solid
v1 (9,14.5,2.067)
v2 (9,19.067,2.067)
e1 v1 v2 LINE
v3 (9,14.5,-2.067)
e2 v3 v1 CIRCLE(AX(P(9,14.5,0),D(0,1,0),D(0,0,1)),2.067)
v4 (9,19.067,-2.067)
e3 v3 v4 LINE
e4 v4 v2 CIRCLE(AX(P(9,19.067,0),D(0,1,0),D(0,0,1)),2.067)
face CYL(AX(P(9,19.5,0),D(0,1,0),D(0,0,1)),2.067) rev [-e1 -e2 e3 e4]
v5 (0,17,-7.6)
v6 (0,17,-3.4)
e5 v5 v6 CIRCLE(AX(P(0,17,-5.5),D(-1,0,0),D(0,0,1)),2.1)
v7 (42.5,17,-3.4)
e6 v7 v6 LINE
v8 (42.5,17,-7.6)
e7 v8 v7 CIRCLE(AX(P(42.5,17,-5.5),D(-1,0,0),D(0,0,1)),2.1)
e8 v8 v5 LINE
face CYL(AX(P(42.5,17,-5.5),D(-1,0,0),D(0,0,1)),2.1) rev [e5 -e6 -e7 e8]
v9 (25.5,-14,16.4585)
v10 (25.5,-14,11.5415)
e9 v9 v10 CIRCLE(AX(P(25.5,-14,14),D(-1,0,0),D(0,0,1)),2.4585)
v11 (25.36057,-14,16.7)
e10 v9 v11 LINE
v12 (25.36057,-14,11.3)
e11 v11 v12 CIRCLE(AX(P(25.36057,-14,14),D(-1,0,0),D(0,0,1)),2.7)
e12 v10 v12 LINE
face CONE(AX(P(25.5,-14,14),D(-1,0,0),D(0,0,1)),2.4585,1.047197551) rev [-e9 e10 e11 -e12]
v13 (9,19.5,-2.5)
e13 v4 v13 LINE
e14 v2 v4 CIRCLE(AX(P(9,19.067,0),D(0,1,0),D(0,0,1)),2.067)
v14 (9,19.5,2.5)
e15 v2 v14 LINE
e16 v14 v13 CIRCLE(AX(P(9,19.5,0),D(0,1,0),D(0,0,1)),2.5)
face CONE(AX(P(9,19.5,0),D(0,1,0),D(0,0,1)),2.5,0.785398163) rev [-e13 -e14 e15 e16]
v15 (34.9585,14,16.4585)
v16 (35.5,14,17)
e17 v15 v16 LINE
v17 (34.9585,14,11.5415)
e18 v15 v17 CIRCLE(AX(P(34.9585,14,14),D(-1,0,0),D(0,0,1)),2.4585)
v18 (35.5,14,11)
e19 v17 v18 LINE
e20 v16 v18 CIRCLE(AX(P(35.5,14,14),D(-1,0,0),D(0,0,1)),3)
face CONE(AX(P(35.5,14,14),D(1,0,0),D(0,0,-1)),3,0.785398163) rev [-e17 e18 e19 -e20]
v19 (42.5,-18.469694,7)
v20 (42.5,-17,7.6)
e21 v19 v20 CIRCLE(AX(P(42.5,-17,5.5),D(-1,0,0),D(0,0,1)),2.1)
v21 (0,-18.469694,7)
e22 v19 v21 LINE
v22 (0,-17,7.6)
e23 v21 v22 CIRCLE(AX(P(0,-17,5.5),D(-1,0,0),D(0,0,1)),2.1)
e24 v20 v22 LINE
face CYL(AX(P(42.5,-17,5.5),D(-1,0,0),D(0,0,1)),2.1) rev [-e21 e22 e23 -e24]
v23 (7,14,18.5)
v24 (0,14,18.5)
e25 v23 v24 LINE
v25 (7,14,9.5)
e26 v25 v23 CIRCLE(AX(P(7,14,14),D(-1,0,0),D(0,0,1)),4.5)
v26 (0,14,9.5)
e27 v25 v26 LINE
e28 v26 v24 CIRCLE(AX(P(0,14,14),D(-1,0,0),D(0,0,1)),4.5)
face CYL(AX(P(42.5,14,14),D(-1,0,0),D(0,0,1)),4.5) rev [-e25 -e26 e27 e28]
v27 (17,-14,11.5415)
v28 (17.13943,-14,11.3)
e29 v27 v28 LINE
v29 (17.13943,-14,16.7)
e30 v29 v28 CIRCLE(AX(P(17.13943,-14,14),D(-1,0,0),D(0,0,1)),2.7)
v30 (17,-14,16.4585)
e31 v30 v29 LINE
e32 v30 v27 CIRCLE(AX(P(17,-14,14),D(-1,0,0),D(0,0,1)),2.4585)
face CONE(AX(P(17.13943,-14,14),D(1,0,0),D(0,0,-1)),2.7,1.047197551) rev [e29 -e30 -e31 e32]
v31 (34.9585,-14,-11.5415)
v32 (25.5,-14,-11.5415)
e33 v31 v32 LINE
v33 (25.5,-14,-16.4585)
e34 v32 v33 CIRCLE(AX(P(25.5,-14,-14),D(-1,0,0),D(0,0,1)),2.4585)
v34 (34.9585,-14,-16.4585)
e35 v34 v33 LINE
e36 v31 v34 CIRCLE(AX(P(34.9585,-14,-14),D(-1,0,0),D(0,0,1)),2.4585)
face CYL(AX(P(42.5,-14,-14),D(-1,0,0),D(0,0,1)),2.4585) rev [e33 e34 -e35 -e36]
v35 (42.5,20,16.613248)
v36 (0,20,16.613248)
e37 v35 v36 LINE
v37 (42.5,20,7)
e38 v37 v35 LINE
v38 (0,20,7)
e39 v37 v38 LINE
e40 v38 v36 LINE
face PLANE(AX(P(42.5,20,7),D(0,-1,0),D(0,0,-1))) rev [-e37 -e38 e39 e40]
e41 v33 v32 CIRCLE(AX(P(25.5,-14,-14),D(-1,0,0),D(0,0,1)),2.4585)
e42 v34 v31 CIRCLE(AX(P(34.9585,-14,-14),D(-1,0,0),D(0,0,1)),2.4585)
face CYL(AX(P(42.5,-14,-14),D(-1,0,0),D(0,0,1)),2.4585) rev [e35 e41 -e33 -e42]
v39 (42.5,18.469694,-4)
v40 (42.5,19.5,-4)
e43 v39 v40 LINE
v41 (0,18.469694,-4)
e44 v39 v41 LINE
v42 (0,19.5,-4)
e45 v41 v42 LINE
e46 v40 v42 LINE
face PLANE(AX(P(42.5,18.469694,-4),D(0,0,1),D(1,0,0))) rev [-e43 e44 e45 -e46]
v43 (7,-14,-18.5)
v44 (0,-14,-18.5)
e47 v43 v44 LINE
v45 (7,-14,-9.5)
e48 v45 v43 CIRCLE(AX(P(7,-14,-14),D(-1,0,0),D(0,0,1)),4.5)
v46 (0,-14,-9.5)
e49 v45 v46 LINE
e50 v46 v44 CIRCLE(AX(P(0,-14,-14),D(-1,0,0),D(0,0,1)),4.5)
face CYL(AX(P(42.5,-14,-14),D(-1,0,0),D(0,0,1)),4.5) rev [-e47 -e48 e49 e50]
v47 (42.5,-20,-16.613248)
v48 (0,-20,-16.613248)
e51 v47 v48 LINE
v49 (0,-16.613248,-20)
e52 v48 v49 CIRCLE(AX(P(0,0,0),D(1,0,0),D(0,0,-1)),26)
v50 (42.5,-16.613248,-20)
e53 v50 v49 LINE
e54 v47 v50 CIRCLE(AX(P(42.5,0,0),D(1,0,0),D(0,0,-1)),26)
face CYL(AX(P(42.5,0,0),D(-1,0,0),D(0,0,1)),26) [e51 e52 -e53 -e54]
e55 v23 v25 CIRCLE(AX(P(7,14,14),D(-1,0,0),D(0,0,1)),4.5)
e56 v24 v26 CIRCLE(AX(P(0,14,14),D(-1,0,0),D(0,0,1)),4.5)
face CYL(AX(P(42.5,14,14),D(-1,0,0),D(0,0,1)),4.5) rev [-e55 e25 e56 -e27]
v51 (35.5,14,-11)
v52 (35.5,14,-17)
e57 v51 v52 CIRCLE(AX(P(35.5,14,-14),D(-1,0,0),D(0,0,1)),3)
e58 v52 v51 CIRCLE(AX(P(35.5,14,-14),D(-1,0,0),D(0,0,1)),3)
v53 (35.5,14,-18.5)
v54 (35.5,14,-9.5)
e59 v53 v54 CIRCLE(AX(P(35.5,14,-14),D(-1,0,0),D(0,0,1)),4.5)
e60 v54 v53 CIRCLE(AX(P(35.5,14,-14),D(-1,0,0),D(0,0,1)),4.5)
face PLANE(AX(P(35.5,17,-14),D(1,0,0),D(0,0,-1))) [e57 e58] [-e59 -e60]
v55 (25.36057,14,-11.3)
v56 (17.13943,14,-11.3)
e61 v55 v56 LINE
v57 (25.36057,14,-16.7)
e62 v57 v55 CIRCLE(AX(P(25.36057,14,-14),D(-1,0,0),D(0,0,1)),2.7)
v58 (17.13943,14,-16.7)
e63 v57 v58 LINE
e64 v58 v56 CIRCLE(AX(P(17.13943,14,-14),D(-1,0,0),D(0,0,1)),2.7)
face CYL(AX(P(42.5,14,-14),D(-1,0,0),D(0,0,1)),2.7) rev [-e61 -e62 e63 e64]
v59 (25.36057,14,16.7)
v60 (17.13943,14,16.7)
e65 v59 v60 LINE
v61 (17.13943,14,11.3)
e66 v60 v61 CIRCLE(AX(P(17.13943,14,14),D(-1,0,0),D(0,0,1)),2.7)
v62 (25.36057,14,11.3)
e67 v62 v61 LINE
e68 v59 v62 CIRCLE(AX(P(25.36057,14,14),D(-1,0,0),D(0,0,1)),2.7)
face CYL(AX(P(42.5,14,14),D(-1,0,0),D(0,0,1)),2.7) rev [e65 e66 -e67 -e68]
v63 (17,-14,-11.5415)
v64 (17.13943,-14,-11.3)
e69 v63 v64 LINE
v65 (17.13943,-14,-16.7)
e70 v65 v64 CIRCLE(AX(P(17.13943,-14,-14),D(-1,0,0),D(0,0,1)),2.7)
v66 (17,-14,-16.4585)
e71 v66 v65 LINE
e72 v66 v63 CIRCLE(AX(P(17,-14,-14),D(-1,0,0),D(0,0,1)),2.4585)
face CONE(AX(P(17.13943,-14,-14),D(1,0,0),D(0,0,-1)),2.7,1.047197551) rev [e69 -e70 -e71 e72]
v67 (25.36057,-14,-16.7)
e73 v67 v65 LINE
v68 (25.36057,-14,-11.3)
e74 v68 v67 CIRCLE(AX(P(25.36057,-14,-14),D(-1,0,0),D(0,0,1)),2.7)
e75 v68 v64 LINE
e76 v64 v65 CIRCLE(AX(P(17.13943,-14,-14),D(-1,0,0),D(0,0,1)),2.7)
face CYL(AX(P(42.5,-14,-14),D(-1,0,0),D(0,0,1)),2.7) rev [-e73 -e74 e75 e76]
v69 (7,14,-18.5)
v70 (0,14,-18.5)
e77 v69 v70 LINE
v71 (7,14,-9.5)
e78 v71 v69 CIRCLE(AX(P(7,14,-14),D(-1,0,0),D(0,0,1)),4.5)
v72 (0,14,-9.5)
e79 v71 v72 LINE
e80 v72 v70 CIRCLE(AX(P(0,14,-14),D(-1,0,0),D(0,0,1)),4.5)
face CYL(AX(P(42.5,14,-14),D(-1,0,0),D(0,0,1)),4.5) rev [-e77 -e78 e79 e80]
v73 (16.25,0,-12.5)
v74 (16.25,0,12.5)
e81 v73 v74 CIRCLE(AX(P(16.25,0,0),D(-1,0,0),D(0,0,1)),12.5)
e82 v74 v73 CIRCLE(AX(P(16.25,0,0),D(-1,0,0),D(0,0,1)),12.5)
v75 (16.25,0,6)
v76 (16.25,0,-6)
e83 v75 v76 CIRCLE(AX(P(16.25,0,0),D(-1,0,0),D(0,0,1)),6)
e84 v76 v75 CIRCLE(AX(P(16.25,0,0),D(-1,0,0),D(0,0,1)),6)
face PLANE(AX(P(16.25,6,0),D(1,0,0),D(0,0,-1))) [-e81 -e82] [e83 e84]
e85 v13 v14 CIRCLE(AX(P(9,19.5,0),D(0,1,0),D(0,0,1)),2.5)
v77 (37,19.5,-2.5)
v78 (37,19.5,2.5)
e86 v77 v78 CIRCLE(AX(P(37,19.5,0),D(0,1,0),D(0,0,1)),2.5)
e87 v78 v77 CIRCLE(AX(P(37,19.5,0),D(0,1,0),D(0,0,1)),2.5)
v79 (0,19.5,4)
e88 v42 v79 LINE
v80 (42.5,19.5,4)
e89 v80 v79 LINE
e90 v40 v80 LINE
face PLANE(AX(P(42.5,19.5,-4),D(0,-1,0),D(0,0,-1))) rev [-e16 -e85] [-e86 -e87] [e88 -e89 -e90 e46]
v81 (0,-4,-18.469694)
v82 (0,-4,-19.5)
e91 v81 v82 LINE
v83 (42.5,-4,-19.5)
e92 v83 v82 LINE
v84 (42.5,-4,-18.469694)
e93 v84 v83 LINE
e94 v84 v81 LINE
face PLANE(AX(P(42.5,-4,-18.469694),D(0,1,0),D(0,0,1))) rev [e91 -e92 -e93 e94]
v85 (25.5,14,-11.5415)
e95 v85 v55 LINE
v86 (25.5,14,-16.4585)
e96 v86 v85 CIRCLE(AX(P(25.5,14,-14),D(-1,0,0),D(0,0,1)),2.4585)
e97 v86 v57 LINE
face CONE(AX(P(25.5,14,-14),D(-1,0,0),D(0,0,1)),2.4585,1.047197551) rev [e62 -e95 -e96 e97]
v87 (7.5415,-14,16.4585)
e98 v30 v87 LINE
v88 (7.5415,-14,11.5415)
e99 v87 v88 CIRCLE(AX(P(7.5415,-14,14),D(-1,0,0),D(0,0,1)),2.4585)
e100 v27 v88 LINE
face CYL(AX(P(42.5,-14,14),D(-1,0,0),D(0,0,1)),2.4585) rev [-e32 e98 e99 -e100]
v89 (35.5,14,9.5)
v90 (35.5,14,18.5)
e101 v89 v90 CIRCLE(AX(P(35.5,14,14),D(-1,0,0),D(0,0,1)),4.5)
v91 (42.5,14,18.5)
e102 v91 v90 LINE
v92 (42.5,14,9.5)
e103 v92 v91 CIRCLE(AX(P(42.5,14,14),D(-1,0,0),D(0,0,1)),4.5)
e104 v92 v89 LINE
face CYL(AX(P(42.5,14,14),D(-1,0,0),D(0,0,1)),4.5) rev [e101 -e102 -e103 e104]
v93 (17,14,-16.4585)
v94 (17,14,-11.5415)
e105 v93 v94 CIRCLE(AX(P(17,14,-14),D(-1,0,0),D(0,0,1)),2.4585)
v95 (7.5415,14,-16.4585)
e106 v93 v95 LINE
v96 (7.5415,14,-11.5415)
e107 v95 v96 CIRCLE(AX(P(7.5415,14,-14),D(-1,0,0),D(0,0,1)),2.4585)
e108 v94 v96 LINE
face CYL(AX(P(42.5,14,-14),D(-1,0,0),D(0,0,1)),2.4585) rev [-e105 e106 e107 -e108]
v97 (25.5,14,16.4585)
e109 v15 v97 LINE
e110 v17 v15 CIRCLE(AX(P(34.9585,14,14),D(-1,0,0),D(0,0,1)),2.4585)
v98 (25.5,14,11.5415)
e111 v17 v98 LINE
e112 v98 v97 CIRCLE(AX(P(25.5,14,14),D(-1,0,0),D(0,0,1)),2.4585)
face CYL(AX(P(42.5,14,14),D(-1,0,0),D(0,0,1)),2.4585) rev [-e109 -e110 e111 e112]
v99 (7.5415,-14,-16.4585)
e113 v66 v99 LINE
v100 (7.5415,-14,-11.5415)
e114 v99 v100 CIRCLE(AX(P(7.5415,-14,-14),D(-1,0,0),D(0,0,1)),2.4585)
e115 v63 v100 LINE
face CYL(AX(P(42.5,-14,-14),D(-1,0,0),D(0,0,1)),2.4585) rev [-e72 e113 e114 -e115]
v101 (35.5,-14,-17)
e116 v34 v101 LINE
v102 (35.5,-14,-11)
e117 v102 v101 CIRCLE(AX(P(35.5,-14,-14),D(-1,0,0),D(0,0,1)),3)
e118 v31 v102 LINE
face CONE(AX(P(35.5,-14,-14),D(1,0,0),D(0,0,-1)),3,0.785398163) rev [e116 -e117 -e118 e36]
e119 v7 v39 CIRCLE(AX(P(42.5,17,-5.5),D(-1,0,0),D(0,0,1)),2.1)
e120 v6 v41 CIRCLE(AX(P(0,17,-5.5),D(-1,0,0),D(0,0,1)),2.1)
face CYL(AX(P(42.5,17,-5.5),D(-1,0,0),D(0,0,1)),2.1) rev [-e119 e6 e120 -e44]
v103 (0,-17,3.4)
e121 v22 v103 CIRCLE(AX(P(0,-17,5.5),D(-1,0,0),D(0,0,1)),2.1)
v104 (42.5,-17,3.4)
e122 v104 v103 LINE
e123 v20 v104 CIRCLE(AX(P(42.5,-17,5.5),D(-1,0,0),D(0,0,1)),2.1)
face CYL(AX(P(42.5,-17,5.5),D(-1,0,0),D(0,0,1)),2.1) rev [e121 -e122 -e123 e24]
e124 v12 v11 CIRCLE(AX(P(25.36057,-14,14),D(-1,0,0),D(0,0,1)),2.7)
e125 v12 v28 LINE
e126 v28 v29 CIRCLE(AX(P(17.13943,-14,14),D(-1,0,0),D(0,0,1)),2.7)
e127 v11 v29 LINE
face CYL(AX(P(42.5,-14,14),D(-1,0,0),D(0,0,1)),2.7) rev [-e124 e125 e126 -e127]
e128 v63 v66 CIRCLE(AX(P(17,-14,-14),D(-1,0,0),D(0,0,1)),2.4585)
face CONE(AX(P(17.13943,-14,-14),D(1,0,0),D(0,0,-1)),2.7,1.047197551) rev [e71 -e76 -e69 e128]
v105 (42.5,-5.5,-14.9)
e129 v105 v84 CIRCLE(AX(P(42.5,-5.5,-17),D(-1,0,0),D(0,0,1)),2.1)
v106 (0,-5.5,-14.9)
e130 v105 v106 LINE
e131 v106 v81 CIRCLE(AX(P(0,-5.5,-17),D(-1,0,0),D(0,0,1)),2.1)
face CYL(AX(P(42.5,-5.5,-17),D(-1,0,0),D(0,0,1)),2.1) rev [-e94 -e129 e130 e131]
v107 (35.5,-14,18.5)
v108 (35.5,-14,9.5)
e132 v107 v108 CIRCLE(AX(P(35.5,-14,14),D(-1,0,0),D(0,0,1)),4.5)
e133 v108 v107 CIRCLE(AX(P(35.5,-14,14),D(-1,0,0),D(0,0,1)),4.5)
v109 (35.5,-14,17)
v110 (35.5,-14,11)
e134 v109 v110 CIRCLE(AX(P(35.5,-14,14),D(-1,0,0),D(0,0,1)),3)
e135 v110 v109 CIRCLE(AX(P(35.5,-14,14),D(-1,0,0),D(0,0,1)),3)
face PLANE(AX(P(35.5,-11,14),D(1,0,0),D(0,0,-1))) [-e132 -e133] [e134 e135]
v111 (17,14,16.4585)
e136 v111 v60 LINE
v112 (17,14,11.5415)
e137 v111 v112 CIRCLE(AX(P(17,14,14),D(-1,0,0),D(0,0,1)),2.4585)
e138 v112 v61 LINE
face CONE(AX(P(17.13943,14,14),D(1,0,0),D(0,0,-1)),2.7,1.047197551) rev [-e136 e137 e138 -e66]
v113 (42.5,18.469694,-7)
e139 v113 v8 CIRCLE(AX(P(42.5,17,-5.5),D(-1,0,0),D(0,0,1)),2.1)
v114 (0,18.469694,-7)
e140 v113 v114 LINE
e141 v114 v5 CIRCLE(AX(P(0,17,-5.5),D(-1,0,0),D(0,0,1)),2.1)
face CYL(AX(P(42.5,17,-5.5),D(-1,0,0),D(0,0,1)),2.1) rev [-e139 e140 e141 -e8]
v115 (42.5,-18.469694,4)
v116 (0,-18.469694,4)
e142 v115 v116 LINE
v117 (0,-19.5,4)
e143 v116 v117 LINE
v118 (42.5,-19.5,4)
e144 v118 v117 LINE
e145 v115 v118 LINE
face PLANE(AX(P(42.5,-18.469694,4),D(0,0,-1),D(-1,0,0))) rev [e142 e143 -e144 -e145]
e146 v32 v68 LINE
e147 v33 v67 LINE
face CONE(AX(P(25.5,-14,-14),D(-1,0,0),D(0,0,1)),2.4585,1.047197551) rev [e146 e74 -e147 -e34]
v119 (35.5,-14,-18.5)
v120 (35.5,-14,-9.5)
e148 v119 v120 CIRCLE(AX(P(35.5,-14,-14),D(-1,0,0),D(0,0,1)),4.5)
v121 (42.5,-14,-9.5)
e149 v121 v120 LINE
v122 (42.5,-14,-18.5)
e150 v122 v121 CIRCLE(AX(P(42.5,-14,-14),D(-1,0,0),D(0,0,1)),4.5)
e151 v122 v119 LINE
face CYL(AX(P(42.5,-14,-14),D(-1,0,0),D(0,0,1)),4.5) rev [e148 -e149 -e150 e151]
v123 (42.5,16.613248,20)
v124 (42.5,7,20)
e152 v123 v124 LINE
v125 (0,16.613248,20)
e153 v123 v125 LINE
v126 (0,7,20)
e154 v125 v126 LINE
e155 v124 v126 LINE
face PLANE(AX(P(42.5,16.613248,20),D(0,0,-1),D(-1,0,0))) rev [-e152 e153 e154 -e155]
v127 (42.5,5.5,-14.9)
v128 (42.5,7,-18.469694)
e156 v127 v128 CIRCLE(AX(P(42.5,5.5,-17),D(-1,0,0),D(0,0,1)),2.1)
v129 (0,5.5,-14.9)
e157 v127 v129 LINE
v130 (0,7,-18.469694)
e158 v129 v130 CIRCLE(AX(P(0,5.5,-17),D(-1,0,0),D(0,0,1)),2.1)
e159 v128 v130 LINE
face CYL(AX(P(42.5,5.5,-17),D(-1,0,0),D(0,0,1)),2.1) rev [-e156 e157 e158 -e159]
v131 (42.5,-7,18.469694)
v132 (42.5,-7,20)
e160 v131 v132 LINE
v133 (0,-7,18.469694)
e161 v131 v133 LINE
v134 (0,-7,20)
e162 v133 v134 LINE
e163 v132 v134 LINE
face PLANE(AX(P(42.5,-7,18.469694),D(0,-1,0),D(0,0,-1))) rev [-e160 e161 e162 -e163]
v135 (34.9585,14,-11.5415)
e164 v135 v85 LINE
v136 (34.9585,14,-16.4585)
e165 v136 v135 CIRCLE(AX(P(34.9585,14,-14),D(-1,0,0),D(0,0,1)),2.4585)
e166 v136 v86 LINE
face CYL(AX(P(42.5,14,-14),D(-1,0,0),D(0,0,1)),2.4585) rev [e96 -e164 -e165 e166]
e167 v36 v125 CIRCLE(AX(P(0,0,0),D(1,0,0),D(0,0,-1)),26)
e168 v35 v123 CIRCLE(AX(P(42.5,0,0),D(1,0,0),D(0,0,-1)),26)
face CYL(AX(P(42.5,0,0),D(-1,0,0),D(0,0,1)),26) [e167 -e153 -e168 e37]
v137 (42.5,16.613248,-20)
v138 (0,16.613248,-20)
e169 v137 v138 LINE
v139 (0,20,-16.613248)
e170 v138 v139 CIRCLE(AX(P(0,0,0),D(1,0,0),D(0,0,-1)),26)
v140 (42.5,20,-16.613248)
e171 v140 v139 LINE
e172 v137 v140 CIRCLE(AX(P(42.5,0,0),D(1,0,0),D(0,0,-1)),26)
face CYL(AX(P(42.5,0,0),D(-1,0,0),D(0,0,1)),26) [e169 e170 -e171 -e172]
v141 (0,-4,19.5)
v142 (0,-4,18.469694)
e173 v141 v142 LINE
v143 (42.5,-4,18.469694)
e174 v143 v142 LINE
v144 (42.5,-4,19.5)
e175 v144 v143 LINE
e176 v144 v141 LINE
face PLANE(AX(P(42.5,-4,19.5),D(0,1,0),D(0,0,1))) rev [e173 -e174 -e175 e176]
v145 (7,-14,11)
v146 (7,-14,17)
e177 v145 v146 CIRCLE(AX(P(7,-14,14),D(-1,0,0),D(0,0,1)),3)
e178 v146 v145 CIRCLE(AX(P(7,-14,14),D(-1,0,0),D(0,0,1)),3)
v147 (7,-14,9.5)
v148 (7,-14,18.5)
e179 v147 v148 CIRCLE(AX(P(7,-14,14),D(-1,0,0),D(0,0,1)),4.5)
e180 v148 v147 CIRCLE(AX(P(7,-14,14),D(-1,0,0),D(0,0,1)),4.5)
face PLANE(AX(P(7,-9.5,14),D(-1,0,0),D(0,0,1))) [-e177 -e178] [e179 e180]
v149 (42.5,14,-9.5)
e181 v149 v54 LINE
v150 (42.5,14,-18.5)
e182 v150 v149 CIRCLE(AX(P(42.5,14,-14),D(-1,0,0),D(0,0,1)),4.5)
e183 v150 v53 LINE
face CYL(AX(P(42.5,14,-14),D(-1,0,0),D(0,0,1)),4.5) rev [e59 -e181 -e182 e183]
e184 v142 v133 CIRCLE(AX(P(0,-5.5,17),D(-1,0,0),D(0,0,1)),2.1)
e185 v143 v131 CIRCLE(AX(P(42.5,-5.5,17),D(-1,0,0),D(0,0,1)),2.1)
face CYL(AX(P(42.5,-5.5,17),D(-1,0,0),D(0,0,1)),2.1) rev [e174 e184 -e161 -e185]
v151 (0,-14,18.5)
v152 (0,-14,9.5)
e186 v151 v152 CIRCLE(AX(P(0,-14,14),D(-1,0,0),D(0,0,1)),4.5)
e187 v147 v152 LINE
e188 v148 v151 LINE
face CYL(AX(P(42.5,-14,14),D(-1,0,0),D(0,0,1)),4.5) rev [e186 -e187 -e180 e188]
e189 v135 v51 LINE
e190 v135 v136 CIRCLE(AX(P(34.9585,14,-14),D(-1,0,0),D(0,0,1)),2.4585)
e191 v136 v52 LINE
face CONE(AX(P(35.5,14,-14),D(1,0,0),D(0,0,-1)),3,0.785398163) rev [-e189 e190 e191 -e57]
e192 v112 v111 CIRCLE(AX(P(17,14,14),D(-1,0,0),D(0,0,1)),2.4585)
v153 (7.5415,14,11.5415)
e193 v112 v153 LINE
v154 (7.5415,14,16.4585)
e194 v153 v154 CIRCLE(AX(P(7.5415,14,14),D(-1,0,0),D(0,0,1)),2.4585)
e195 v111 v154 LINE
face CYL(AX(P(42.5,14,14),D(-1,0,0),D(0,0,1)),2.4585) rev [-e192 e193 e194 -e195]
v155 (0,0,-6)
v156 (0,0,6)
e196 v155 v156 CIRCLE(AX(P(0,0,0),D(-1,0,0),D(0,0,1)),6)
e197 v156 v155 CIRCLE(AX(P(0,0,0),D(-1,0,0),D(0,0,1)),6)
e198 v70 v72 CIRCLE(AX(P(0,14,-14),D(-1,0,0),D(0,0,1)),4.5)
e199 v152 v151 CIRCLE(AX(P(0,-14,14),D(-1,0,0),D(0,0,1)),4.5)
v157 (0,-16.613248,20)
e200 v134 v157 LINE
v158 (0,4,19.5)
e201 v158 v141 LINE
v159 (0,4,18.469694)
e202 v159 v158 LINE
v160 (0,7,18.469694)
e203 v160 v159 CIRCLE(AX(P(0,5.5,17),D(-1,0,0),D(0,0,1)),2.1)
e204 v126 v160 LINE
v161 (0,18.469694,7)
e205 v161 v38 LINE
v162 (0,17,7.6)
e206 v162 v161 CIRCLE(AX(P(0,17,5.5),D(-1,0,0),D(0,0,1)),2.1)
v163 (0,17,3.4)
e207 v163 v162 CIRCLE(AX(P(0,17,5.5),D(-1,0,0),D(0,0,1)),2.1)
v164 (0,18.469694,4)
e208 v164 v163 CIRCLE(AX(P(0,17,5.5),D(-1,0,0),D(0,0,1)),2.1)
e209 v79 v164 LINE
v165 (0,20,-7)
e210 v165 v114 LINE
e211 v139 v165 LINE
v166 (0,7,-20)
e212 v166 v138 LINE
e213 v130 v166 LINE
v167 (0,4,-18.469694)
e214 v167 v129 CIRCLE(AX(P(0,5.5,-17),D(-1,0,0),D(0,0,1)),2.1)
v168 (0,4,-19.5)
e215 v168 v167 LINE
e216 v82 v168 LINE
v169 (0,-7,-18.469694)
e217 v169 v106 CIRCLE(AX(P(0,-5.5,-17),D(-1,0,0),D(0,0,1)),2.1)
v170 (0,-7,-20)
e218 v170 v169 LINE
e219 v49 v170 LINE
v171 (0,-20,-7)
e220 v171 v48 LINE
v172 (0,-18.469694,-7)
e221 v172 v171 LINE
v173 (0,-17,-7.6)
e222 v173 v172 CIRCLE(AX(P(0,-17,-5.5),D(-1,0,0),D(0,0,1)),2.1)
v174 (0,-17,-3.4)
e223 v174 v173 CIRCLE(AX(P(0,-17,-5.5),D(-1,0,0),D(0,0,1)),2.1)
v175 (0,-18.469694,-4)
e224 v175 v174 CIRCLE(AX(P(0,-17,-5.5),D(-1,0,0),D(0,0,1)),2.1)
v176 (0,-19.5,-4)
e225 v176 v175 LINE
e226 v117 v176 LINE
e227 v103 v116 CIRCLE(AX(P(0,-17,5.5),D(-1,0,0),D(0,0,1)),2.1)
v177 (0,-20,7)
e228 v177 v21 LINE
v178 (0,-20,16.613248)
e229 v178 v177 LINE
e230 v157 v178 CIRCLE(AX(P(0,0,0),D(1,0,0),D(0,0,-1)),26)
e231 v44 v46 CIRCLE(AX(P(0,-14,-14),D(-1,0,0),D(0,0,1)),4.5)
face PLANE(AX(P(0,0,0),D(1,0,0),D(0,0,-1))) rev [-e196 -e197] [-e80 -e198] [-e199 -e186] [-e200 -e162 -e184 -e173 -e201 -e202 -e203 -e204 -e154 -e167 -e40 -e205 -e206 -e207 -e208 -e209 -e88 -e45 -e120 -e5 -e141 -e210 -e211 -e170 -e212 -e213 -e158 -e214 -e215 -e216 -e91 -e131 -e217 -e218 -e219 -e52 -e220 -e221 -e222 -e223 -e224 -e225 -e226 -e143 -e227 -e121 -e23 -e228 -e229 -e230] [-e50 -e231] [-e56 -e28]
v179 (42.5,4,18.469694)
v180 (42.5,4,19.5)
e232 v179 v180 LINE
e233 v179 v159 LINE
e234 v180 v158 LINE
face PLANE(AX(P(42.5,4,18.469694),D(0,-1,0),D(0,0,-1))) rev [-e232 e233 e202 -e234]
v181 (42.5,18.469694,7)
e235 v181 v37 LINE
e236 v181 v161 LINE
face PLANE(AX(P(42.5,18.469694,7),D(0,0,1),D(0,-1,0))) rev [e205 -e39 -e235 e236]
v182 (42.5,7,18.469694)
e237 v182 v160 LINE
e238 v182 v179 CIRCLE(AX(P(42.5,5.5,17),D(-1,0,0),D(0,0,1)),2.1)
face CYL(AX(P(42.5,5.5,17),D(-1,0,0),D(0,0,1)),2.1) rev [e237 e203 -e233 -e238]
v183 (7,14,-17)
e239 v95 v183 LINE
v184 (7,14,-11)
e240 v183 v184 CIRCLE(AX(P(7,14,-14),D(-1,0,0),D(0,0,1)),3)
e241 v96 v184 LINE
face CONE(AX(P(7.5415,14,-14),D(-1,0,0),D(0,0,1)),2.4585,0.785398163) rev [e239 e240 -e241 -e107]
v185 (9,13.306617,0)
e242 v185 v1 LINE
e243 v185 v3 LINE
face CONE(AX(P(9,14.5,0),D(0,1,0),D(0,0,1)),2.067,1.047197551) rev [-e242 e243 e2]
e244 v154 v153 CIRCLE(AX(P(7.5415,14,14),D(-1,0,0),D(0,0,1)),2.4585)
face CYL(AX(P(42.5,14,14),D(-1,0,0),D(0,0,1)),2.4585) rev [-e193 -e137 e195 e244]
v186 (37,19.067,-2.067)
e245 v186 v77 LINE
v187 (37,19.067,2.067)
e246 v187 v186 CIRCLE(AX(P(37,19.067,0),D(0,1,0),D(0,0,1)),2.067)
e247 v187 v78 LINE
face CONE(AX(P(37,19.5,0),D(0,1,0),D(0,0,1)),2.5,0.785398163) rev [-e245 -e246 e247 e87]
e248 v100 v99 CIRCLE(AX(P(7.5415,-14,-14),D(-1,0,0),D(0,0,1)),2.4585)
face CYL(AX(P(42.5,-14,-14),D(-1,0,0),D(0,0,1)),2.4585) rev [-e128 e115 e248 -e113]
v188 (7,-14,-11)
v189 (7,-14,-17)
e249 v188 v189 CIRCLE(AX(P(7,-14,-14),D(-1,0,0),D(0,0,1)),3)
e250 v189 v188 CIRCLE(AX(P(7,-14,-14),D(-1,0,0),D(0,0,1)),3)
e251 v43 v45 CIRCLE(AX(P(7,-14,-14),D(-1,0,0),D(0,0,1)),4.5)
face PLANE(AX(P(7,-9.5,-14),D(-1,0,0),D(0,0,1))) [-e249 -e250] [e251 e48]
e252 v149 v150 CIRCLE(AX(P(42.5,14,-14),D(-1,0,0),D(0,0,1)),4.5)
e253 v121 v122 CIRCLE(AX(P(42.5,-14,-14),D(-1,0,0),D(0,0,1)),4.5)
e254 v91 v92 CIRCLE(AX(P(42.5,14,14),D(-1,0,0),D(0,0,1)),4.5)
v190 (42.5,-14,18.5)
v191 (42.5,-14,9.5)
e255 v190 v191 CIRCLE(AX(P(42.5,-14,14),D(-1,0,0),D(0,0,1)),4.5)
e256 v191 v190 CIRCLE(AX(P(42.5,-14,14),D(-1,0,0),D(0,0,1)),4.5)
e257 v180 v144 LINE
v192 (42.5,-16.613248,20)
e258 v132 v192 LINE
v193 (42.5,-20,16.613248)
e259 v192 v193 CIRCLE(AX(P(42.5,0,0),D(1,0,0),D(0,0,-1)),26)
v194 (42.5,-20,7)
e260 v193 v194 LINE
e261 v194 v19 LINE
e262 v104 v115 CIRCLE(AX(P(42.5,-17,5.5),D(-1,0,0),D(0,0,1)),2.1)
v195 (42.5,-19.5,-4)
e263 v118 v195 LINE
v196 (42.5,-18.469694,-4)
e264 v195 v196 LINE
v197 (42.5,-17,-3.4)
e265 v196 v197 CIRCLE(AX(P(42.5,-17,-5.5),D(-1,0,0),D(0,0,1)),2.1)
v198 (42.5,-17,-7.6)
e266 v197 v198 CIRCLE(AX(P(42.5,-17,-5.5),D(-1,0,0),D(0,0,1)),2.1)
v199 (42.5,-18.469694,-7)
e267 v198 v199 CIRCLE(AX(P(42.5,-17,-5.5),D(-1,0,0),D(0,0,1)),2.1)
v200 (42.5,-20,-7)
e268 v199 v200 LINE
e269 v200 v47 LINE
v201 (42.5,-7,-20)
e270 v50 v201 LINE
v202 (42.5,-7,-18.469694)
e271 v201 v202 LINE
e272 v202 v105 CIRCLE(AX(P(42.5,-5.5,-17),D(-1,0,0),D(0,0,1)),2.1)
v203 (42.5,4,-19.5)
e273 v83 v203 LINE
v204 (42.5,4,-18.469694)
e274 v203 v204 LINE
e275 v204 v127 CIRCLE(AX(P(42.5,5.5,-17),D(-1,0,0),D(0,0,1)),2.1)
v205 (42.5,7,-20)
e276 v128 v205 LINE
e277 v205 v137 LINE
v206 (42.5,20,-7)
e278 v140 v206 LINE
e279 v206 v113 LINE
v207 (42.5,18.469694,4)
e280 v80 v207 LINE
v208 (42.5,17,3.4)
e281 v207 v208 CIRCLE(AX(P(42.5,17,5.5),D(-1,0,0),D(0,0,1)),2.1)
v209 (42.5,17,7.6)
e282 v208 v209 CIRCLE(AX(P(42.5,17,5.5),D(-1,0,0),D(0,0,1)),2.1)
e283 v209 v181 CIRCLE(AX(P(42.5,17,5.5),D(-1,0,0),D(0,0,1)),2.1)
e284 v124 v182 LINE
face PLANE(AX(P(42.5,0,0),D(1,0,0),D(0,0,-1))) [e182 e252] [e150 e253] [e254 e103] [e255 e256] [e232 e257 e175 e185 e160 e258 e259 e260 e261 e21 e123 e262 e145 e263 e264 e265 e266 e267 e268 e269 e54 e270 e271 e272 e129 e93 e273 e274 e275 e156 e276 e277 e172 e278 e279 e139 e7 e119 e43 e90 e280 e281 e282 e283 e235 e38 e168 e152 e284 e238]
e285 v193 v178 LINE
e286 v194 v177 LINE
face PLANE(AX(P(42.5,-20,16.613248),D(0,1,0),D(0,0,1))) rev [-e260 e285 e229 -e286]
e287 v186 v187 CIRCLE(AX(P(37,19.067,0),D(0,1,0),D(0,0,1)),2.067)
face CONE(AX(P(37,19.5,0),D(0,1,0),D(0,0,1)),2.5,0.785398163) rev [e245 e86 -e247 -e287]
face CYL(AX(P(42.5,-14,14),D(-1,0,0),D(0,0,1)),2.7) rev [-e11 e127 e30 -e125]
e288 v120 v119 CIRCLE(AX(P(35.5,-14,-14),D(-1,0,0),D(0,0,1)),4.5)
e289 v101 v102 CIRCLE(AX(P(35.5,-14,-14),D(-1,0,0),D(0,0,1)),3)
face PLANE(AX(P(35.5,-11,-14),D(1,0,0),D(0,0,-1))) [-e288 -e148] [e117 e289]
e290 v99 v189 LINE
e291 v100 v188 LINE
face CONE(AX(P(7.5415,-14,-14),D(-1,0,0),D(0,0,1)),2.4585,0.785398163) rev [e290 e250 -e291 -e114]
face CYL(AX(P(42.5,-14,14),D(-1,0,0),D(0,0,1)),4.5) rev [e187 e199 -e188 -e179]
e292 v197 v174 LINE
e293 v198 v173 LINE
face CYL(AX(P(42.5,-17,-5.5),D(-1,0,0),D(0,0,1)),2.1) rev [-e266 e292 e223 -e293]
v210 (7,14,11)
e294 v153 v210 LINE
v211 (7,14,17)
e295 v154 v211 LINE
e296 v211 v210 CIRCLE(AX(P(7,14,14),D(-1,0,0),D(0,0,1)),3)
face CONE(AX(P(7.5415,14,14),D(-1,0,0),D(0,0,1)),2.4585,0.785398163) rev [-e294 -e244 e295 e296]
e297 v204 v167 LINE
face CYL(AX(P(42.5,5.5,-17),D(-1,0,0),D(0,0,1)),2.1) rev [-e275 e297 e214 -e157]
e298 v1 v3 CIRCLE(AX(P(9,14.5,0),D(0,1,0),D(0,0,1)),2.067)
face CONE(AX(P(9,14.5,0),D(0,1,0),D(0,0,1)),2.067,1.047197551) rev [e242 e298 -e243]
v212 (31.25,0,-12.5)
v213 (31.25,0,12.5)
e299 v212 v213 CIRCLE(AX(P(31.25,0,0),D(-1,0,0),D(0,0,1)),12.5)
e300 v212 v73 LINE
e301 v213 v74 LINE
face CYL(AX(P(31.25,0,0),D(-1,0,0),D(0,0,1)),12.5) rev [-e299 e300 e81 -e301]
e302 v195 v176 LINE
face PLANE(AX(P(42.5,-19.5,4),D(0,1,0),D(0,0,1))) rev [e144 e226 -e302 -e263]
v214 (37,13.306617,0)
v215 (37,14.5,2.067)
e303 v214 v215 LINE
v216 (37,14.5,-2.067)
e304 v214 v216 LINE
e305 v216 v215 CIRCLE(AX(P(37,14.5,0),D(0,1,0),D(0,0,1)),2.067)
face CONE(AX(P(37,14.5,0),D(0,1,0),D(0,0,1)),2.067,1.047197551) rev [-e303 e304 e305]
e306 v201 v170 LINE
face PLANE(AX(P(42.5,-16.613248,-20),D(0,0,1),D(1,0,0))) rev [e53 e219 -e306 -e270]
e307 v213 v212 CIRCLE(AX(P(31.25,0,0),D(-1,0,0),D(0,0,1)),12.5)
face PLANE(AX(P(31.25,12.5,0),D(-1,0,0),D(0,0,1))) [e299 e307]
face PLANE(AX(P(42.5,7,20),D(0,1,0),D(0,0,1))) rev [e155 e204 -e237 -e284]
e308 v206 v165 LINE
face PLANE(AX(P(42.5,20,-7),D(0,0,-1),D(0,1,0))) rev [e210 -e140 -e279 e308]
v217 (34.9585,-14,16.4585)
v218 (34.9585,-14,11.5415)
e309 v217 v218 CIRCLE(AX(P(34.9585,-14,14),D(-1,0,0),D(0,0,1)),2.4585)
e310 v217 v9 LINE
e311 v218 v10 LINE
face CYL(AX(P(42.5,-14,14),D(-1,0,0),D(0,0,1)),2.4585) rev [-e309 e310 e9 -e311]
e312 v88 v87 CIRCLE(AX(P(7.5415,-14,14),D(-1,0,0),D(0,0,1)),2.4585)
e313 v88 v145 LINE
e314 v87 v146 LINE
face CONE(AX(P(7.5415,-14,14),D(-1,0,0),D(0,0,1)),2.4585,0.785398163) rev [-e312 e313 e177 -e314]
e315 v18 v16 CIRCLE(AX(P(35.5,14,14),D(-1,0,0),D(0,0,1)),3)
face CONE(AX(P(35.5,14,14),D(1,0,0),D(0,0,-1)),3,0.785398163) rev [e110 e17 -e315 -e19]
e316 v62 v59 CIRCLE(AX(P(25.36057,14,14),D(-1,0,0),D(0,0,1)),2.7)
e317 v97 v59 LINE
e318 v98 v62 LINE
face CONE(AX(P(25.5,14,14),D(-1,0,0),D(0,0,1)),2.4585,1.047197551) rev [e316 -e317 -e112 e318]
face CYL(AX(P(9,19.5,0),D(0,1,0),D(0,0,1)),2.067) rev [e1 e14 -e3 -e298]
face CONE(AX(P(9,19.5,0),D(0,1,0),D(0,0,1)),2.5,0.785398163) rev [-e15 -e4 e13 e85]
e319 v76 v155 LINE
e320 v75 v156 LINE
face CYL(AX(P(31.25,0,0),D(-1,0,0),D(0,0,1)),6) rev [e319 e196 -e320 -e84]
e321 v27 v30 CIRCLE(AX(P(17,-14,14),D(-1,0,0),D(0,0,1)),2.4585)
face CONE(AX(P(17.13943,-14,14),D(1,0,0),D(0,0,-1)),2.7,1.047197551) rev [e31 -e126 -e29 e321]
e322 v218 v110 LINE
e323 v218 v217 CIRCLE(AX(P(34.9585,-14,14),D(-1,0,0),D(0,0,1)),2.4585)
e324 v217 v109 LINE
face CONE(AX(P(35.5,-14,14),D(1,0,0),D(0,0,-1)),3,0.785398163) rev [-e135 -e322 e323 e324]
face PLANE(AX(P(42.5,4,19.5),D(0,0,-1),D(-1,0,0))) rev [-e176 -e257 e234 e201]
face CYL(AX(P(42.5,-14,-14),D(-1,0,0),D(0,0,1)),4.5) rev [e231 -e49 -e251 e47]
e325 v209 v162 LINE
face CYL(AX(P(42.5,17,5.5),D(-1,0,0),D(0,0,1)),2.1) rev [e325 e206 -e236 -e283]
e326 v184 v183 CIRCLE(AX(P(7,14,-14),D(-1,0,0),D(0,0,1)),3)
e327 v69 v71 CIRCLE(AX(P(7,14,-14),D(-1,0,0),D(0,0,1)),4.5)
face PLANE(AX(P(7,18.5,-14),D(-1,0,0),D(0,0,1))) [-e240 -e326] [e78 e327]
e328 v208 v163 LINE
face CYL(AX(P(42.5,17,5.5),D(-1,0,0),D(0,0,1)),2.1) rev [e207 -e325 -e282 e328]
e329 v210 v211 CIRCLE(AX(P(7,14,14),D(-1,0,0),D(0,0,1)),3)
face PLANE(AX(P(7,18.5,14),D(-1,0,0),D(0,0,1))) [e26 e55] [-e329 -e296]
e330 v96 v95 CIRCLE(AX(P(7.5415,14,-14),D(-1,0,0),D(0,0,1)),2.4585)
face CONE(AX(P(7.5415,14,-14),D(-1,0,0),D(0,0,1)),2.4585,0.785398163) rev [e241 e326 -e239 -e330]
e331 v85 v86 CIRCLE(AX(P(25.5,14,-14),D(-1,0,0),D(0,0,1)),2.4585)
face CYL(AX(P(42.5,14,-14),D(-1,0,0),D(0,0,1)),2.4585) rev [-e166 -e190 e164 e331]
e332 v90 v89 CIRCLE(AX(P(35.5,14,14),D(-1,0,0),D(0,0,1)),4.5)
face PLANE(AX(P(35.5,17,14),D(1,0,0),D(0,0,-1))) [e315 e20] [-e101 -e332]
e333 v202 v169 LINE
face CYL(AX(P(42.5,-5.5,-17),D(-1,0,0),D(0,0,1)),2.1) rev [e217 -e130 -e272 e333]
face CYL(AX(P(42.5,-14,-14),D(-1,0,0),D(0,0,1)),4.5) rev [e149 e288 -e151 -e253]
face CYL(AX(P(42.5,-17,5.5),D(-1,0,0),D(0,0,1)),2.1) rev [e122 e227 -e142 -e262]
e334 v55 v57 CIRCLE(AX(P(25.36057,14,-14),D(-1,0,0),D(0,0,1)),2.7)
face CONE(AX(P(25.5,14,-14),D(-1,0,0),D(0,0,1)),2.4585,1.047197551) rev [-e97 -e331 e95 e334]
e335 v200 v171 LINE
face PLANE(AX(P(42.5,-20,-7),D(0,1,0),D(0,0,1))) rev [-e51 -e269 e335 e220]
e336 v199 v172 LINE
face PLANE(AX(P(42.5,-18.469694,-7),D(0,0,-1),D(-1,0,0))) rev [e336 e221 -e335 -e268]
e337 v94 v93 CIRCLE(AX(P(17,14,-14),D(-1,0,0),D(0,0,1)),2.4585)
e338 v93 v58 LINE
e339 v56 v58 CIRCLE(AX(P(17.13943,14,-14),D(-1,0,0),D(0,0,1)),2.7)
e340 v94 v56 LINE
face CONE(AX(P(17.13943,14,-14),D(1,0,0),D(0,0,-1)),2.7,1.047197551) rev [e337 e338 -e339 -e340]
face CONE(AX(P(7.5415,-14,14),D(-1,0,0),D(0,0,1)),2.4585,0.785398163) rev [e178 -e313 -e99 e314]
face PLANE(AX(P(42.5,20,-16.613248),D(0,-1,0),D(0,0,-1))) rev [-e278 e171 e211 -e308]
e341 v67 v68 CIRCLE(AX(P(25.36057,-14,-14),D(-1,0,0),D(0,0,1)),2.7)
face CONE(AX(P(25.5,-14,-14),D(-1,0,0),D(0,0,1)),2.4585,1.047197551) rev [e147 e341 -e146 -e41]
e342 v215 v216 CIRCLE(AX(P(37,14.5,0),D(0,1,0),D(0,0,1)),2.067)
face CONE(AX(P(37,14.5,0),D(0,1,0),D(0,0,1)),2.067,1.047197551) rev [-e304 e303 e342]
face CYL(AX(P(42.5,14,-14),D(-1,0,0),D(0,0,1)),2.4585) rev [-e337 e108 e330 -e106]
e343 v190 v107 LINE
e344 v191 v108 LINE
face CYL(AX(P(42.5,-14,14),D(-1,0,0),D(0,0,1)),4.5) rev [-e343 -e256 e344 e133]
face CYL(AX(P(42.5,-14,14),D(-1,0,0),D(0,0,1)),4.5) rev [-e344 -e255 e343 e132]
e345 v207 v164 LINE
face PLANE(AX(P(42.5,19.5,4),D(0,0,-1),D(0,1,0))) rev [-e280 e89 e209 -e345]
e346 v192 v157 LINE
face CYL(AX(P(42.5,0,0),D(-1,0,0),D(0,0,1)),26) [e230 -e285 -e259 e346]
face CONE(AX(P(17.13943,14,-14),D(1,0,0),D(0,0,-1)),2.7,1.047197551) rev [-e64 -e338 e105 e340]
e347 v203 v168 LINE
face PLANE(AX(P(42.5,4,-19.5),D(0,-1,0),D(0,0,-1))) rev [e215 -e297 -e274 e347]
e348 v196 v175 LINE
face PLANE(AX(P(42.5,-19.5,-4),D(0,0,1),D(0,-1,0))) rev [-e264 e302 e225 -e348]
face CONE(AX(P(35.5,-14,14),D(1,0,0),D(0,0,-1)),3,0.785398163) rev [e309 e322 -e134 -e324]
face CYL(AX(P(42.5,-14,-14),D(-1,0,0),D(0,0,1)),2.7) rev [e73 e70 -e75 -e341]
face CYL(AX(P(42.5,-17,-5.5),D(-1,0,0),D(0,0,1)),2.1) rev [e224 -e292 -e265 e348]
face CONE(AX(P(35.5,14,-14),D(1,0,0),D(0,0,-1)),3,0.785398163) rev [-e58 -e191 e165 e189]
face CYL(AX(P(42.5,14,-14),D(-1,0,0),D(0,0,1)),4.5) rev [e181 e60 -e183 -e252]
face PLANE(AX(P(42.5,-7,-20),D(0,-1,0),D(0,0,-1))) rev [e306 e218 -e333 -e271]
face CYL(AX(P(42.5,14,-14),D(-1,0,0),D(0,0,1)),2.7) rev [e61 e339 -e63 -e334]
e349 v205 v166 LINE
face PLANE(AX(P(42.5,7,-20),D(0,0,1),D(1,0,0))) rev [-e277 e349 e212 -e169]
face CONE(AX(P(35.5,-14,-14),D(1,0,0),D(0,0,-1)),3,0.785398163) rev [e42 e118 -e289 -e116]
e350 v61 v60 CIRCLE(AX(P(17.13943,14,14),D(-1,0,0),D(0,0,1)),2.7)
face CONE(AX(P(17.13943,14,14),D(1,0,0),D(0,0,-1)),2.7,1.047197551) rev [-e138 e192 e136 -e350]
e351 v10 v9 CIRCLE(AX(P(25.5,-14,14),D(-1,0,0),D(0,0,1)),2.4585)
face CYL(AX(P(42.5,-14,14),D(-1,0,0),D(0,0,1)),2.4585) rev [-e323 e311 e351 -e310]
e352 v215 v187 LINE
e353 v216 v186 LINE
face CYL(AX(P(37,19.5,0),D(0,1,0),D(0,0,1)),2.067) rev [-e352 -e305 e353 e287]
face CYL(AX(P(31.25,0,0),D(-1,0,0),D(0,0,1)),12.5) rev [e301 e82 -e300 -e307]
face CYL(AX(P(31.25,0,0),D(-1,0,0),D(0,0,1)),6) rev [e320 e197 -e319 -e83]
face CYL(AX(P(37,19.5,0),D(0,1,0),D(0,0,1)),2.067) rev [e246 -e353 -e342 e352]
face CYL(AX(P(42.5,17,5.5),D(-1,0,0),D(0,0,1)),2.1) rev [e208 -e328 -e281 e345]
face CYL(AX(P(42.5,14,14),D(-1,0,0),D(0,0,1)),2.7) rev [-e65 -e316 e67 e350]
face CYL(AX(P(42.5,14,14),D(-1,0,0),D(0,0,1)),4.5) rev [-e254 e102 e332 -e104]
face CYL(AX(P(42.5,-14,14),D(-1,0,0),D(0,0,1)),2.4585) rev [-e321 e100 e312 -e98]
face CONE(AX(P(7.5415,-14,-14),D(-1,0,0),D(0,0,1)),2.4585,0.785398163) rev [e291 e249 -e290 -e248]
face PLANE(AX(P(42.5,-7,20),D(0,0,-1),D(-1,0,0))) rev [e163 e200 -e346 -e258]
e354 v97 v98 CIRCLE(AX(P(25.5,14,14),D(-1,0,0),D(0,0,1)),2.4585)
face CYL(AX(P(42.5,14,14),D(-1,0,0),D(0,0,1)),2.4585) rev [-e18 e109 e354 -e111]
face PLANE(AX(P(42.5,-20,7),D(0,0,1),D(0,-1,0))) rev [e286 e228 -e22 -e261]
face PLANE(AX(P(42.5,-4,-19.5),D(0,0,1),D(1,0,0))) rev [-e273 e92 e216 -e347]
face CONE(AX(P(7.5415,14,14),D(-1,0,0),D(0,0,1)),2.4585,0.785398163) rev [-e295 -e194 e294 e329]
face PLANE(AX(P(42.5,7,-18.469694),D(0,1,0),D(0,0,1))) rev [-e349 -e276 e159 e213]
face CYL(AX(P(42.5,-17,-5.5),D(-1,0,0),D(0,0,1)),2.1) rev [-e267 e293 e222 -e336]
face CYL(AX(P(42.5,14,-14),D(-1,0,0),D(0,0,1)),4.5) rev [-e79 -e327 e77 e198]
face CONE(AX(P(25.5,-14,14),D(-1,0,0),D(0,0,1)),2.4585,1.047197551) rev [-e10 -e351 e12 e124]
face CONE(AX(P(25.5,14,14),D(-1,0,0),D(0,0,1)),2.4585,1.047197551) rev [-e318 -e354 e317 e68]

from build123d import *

# Parameters (mm, degrees)
BOSS_EXTRUDE1_DEPTH  = 42.5
LPATTERN1_COUNT      = 2
LPATTERN1_PITCH      = 28
LPATTERN1_COUNT_DIR2 = 2
LPATTERN1_PITCH_DIR2 = 28
HOLE1_D              = 4.134
HOLE1_DEPTH          = 5
HOLE1_CSINK_D        = 5
HOLE1_CSINK_ANGLE    = 90
HOLE1_TIP            = 1.193383006
HOLE2_D              = 4.134
HOLE2_DEPTH          = 5
HOLE2_CSINK_D        = 5
HOLE2_CSINK_ANGLE    = 90
HOLE2_TIP            = 1.193383006


with BuildPart() as part:
    # Sketch1 → Boss-Extrude1 (new body)
    with BuildSketch(Plane(origin=(0, 0, 0), x_dir=(0, 0, -1), z_dir=(1, 0, 0))):
        with BuildLine():
            Line((-16.613247726, -20), (-7, -20))
            Line((-7, -20), (-7, -18.469693846))
            ThreePointArc((-7, -18.469693846), (-5.5, -14.9), (-4, -18.469693846))
            Line((-4, -18.469693846), (-4, -19.5))
            Line((-4, -19.5), (4, -19.5))
            Line((4, -19.5), (4, -18.469693846))
            ThreePointArc((4, -18.469693846), (5.5, -14.9), (7, -18.469693846))
            Line((7, -18.469693846), (7, -20))
            Line((7, -20), (16.613247726, -20))
            ThreePointArc((16.613247726, -20), (18.384776311, -18.384776311), (20, -16.613247726))
            Line((20, -16.613247726), (20, -7))
            Line((20, -7), (18.469693846, -7))
            ThreePointArc((18.469693846, -7), (14.9, -5.5), (18.469693846, -4))
            Line((18.469693846, -4), (19.5, -4))
            Line((19.5, -4), (19.5, 4))
            Line((19.5, 4), (18.469693846, 4))
            ThreePointArc((18.469693846, 4), (14.9, 5.5), (18.469693846, 7))
            Line((18.469693846, 7), (20, 7))
            Line((20, 7), (20, 16.613247726))
            ThreePointArc((20, 16.613247726), (18.384776311, 18.384776311), (16.613247726, 20))
            Line((16.613247726, 20), (7, 20))
            Line((7, 20), (7, 18.469693846))
            ThreePointArc((7, 18.469693846), (5.5, 14.9), (4, 18.469693846))
            Line((4, 18.469693846), (4, 19.5))
            Line((4, 19.5), (-4, 19.5))
            Line((-4, 19.5), (-4, 18.469693846))
            ThreePointArc((-4, 18.469693846), (-5.5, 14.9), (-7, 18.469693846))
            Line((-7, 18.469693846), (-7, 20))
            Line((-7, 20), (-16.613247726, 20))
            ThreePointArc((-16.613247726, 20), (-18.384776311, 18.384776311), (-20, 16.613247726))
            Line((-20, 16.613247726), (-20, 7))
            Line((-20, 7), (-18.469693846, 7))
            ThreePointArc((-18.469693846, 7), (-14.9, 5.5), (-18.469693846, 4))
            Line((-18.469693846, 4), (-19.5, 4))
            Line((-19.5, 4), (-19.5, -4))
            Line((-19.5, -4), (-18.469693846, -4))
            ThreePointArc((-18.469693846, -4), (-14.9, -5.5), (-18.469693846, -7))
            Line((-18.469693846, -7), (-20, -7))
            Line((-20, -7), (-20, -16.613247726))
            ThreePointArc((-20, -16.613247726), (-18.384776311, -18.384776311), (-16.613247726, -20))
        make_face()
    extrude(amount=BOSS_EXTRUDE1_DEPTH)

    # Sketch2 → Cut-Revolve1 (revolve, cut)
    with BuildSketch(Plane.XY.offset(14), mode=Mode.PRIVATE) as cut_revolve1_sk:
        Polygon((0, 14), (0, 18.5), (7, 18.5), (7, 17), (7.5415, 16.4585), (17, 16.4585), (17.13943009, 16.7), (25.36056991, 16.7), (25.5, 16.4585), (34.9585, 16.4585), (35.5, 17), (35.5, 18.5), (42.5, 18.5), (42.5, 14), align=None)
    cut_revolve1 = revolve(cut_revolve1_sk.sketch.rotate(Axis((42.5, 14, 14), (-1, 0, 0)), 270), axis=Axis((42.5, 14, 14), (-1, 0, 0)), mode=Mode.SUBTRACT)

    # LPattern1: Cut-Revolve1 2 × 2
    with Locations(*[(0, -j * LPATTERN1_PITCH_DIR2, -i * LPATTERN1_PITCH) for i in range(LPATTERN1_COUNT) for j in range(LPATTERN1_COUNT_DIR2) if (i, j) != (0, 0)]):
        add(cut_revolve1, mode=Mode.SUBTRACT)

    # Sketch4 → Cut-Revolve2 (revolve, cut)
    with BuildSketch(Plane.XY, mode=Mode.PRIVATE) as cut_revolve2_sk:
        Polygon((0, 0), (0, 6), (16.25, 6), (16.25, 12.5), (31.25, 12.5), (31.25, 0), align=None)
    revolve(cut_revolve2_sk.sketch.rotate(Axis((31.25, 0, 0), (-1, 0, 0)), 270), axis=Axis((31.25, 0, 0), (-1, 0, 0)), mode=Mode.SUBTRACT)

    # Hole1
    with Locations(Plane(origin=(0, 19.5, 0), x_dir=(-1, 0, 0), z_dir=(0, 1, 0))):
        with Locations((-9, 0)):
            CounterSinkHole(HOLE1_D / 2, HOLE1_CSINK_D / 2, depth=HOLE1_DEPTH, counter_sink_angle=HOLE1_CSINK_ANGLE)
            with Locations((0, 0, -(HOLE1_DEPTH + HOLE1_TIP / 2))):  # 120° drill point
                Cone(0, HOLE1_D / 2, HOLE1_TIP, mode=Mode.SUBTRACT)

    # Hole2
    with Locations(Plane(origin=(0, 19.5, 0), x_dir=(-1, 0, 0), z_dir=(0, 1, 0))):
        with Locations((-37, 0)):
            CounterSinkHole(HOLE2_D / 2, HOLE2_CSINK_D / 2, depth=HOLE2_DEPTH, counter_sink_angle=HOLE2_CSINK_ANGLE)
            with Locations((0, 0, -(HOLE2_DEPTH + HOLE2_TIP / 2))):  # 120° drill point
                Cone(0, HOLE2_D / 2, HOLE2_TIP, mode=Mode.SUBTRACT)


solid = part.part
